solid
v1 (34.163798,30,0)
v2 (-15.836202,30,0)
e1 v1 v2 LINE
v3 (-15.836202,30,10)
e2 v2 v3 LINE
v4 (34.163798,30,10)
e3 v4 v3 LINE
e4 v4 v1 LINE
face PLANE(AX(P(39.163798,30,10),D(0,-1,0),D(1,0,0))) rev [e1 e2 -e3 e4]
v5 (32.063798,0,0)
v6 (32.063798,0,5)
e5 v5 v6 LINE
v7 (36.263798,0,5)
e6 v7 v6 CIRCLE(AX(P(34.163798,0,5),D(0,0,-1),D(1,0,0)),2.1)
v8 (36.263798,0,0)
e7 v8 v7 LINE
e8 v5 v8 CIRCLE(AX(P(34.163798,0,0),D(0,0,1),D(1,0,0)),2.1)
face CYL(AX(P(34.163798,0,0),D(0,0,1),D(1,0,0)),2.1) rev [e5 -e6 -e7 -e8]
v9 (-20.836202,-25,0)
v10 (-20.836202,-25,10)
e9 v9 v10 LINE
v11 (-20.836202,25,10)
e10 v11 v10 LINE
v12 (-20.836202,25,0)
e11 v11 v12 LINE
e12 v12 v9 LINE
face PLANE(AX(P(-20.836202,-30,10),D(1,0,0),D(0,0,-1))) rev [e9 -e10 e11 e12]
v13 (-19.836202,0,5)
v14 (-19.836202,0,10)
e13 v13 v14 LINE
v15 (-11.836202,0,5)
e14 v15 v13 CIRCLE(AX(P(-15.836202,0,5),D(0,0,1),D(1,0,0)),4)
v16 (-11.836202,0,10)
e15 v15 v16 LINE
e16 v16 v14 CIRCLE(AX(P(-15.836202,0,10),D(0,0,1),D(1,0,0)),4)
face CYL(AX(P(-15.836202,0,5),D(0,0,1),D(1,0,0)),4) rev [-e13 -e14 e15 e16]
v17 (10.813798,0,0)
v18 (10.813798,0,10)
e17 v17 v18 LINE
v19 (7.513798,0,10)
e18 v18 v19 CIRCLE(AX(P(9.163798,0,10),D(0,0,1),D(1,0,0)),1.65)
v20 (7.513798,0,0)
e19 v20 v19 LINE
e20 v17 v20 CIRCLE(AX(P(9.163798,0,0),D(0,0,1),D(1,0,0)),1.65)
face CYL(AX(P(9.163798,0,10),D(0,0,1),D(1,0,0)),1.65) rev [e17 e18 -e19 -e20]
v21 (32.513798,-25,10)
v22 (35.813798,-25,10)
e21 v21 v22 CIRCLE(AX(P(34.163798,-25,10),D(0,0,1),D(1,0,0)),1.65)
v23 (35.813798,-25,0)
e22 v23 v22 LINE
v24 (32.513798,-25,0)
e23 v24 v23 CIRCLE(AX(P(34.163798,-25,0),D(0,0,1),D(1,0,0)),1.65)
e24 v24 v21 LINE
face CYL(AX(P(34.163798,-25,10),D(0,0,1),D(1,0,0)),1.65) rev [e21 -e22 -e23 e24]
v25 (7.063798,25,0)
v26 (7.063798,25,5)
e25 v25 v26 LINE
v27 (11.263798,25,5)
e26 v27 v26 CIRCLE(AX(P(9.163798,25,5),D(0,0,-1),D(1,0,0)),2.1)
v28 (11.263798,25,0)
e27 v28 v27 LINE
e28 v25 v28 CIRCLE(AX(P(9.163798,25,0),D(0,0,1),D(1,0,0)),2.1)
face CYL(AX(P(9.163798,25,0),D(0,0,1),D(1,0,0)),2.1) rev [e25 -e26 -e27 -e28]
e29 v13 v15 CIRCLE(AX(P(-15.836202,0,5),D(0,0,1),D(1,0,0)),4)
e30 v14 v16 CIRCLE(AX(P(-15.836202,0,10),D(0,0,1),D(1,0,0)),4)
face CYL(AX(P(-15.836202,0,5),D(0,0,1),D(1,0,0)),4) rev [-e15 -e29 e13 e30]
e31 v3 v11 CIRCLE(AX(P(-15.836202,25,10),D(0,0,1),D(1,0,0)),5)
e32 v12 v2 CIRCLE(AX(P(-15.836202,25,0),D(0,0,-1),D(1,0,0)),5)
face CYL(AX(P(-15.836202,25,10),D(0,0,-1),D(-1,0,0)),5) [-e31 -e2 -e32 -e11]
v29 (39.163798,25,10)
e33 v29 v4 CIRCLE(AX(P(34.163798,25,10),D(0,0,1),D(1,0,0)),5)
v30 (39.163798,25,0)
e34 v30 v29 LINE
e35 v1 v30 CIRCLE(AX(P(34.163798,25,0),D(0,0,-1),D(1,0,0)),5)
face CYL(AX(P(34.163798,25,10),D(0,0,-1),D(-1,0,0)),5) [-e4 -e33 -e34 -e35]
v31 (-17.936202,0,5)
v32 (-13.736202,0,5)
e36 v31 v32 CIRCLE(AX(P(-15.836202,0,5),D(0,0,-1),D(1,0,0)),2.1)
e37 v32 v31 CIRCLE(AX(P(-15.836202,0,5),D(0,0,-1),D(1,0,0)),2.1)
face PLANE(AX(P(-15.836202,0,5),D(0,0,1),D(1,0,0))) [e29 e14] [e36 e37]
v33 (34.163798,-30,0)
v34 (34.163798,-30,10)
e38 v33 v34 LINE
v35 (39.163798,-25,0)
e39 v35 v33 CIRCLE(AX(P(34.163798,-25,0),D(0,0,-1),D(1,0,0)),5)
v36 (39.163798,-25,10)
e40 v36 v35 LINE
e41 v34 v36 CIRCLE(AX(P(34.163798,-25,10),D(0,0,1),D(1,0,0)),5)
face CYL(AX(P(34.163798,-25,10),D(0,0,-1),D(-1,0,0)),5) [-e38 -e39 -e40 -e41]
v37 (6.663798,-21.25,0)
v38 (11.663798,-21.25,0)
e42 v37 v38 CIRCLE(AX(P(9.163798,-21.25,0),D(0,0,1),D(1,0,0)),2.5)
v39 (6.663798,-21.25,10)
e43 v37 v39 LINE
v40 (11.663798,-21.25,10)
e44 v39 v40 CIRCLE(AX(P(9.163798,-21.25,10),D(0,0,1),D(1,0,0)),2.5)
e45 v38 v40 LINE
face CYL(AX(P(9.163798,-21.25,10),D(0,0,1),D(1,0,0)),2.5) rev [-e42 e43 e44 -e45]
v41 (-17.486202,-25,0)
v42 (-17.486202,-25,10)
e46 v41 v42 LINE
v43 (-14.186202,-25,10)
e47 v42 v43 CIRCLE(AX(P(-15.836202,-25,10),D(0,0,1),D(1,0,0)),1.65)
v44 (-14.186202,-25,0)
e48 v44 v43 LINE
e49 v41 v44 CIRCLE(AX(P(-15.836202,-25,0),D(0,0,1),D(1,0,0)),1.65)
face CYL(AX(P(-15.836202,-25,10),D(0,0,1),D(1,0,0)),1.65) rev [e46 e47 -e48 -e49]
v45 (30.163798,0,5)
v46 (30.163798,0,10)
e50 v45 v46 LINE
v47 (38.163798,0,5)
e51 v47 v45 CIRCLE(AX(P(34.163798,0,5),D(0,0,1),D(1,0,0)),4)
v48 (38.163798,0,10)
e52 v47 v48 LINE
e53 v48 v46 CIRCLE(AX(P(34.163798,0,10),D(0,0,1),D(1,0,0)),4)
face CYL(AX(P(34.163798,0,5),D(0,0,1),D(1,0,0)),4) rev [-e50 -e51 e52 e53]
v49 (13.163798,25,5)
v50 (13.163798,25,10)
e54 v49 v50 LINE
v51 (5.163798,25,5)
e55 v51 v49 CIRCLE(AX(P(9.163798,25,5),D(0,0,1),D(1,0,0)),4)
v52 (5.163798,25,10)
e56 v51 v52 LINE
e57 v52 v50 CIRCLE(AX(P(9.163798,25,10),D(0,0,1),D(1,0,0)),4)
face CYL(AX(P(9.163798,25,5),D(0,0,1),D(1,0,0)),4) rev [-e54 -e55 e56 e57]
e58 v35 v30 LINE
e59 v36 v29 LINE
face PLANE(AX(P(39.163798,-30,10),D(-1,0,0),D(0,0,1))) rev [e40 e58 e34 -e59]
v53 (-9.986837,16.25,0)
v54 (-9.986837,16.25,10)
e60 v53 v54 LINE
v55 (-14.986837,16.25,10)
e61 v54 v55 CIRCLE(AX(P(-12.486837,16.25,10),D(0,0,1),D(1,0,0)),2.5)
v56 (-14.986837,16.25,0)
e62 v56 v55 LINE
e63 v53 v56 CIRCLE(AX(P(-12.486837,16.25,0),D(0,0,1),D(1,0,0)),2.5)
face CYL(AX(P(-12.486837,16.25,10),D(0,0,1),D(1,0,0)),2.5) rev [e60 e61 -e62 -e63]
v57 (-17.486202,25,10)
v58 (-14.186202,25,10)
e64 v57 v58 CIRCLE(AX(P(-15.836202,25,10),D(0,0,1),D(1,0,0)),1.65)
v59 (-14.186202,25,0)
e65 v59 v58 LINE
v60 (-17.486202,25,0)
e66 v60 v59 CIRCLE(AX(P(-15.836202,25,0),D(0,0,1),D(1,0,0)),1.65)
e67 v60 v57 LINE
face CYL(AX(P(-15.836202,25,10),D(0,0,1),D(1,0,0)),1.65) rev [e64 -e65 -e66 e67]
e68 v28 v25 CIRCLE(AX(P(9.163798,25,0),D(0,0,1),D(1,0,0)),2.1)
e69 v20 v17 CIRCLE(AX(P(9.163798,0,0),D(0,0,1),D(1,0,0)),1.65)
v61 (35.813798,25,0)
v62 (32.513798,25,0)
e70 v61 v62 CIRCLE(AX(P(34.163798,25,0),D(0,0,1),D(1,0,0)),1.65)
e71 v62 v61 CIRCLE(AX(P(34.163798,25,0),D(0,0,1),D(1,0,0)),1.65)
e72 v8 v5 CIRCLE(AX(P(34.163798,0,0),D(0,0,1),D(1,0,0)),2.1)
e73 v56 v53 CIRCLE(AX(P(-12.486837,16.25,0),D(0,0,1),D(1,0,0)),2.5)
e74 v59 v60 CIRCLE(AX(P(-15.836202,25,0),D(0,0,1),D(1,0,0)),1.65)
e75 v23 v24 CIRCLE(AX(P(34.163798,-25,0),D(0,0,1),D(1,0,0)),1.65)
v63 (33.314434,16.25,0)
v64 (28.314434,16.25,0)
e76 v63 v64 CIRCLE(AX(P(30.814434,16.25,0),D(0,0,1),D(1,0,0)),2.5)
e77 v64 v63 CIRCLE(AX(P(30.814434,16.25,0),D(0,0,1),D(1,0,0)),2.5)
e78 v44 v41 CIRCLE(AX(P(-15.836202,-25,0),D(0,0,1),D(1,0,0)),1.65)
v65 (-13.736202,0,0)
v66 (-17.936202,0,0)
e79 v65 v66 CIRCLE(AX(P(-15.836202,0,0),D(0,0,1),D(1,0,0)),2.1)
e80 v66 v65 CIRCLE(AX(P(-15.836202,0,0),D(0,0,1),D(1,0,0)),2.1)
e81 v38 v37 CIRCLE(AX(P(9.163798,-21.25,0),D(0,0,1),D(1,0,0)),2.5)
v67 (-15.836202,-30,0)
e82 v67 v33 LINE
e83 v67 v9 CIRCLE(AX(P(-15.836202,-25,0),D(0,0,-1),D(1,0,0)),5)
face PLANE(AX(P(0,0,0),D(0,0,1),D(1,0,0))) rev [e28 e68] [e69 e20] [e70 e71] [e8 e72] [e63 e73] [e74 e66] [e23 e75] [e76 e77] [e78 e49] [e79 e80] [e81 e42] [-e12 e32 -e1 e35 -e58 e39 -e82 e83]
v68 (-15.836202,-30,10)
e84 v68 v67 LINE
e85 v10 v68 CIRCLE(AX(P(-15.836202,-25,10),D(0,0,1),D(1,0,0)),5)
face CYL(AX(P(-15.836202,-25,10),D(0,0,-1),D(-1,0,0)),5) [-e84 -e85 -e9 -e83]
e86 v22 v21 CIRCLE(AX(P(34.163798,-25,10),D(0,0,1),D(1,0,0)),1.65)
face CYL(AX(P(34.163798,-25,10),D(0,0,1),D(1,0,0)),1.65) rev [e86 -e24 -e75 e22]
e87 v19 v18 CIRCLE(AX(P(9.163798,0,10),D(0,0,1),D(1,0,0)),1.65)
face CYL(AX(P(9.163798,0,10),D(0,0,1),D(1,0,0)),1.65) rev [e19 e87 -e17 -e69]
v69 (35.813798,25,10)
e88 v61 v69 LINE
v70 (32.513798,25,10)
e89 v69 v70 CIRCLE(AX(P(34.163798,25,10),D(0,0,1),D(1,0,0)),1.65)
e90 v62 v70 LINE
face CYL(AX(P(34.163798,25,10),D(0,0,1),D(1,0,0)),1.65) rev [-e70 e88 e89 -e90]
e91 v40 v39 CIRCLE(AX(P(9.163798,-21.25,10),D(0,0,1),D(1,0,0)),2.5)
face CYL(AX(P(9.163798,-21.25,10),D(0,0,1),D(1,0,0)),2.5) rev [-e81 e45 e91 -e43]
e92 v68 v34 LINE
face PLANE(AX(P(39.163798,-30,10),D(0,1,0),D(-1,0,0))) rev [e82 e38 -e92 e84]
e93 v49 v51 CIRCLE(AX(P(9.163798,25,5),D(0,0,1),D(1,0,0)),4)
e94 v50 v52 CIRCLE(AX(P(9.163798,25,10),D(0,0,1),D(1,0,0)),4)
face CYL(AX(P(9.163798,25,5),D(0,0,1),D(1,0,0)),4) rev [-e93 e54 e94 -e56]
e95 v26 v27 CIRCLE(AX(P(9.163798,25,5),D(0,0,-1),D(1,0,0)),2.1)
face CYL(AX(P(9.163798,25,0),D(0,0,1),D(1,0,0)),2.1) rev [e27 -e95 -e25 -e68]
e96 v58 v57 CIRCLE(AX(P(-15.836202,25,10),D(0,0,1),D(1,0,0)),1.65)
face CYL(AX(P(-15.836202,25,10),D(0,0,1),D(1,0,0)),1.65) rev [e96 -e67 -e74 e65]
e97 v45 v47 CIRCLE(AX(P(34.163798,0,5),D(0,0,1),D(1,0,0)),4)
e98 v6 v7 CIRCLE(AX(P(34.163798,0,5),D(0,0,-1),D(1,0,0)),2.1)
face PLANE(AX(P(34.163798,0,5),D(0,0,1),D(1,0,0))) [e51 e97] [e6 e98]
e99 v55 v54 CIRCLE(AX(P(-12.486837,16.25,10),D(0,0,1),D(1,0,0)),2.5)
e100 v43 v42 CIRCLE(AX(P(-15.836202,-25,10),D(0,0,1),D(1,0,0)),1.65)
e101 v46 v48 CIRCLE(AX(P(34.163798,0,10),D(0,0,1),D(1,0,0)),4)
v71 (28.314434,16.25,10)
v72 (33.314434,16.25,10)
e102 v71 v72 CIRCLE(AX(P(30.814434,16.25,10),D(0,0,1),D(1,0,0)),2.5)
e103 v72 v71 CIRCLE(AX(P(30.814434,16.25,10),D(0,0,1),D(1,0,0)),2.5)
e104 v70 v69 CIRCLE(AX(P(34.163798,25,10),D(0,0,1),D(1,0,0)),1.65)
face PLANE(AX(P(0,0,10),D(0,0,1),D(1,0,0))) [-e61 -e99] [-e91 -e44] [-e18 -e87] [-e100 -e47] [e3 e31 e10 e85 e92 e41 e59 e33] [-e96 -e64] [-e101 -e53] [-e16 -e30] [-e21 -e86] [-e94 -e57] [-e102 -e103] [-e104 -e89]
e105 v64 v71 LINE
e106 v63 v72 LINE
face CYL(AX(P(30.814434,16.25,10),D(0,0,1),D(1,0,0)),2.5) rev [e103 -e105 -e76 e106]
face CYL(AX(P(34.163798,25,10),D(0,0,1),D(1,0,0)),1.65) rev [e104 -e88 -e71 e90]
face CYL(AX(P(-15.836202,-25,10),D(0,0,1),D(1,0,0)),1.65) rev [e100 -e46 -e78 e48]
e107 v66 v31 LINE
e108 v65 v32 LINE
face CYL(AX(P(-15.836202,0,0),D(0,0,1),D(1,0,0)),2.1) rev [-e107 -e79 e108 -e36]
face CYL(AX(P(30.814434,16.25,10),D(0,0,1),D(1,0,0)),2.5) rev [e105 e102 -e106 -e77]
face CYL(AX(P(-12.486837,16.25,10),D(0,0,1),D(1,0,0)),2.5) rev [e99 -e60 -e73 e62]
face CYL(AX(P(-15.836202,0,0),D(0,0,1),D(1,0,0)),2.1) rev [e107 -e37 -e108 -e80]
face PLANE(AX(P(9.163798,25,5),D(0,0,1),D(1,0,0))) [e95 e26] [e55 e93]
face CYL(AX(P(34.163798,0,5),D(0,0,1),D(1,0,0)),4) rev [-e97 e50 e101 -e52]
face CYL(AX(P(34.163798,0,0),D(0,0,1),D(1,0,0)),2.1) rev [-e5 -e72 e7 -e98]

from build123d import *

# Parameters (mm, degrees)
SKETCH1_W             = 60
SKETCH1_H             = 60
BOSS_EXTRUDE1_DEPTH   = 10
FILLET1_R             = 5
M6_TAPPED_HOLE1_D     = 5
M6_TAPPED_HOLE1_DEPTH = 15
M6_TAPPED_HOLE1_TIP   = 1.502151548
SKETCH8_R             = 2.1
CUT_EXTRUDE1_DEPTH    = 51.336896077
SKETCH9_R             = 4
CUT_EXTRUDE2_DEPTH    = 5
M4_TAPPED_HOLE1_D     = 3.3
M4_TAPPED_HOLE2_D     = 3.3


with BuildPart() as part:
    # Sketch1 → Boss-Extrude1 (new body)
    with BuildSketch(Plane.XY):
        with Locations((9.163798419, 0)):
            Rectangle(SKETCH1_W, SKETCH1_H)
    extrude(amount=BOSS_EXTRUDE1_DEPTH)

    # Fillet1
    fillet1_edges = [part.edges().sort_by_distance(p)[0] for p in [
        (-20.836201581, 30, 5),
        (39.163798419, 30, 5),
        (39.163798419, -30, 5),
        (-20.836201581, -30, 5),
    ]]
    fillet(fillet1_edges, radius=FILLET1_R)

    # M6 Tapped Hole1
    with Locations(Plane.XY.offset(10)):
        with Locations((9.163798419, -21.25), (30.814433514, 16.25), (-12.486836675, 16.25)):
            Hole(M6_TAPPED_HOLE1_D / 2, depth=M6_TAPPED_HOLE1_DEPTH)
            with Locations((0, 0, -(M6_TAPPED_HOLE1_DEPTH + M6_TAPPED_HOLE1_TIP / 2))):  # 118° drill point
                Cone(0, M6_TAPPED_HOLE1_D / 2, M6_TAPPED_HOLE1_TIP, mode=Mode.SUBTRACT)

    # Sketch8 → Cut-Extrude1 (cut, through all)
    with BuildSketch(Plane.XY.offset(10)):
        with Locations((9.163798419, 25)):
            Circle(SKETCH8_R)
        with Locations((34.163798419, 0)):
            Circle(SKETCH8_R)
        with Locations((-15.836201581, 0)):
            Circle(SKETCH8_R)
    extrude(amount=-CUT_EXTRUDE1_DEPTH, mode=Mode.SUBTRACT)

    # Sketch9 → Cut-Extrude2 (cut)
    with BuildSketch(Plane.XY.offset(10)):
        with Locations((-15.836201581, 0)):
            Circle(SKETCH9_R)
        with Locations((9.163798419, 25)):
            Circle(SKETCH9_R)
        with Locations((34.163798419, 0)):
            Circle(SKETCH9_R)
    extrude(amount=-CUT_EXTRUDE2_DEPTH, mode=Mode.SUBTRACT)

    # M4 Tapped Hole1 (through all)
    with Locations(Plane.XY.offset(10)):
        with Locations((-15.836201581, -25), (34.163798419, -25), (34.163798419, 25), (-15.836201581, 25)):
            Hole(M4_TAPPED_HOLE1_D / 2)

    # M4 Tapped Hole2 (through all)
    with Locations(Plane.XY.offset(10)):
        with Locations((9.163798419, 0)):
            Hole(M4_TAPPED_HOLE2_D / 2)


solid = part.part
